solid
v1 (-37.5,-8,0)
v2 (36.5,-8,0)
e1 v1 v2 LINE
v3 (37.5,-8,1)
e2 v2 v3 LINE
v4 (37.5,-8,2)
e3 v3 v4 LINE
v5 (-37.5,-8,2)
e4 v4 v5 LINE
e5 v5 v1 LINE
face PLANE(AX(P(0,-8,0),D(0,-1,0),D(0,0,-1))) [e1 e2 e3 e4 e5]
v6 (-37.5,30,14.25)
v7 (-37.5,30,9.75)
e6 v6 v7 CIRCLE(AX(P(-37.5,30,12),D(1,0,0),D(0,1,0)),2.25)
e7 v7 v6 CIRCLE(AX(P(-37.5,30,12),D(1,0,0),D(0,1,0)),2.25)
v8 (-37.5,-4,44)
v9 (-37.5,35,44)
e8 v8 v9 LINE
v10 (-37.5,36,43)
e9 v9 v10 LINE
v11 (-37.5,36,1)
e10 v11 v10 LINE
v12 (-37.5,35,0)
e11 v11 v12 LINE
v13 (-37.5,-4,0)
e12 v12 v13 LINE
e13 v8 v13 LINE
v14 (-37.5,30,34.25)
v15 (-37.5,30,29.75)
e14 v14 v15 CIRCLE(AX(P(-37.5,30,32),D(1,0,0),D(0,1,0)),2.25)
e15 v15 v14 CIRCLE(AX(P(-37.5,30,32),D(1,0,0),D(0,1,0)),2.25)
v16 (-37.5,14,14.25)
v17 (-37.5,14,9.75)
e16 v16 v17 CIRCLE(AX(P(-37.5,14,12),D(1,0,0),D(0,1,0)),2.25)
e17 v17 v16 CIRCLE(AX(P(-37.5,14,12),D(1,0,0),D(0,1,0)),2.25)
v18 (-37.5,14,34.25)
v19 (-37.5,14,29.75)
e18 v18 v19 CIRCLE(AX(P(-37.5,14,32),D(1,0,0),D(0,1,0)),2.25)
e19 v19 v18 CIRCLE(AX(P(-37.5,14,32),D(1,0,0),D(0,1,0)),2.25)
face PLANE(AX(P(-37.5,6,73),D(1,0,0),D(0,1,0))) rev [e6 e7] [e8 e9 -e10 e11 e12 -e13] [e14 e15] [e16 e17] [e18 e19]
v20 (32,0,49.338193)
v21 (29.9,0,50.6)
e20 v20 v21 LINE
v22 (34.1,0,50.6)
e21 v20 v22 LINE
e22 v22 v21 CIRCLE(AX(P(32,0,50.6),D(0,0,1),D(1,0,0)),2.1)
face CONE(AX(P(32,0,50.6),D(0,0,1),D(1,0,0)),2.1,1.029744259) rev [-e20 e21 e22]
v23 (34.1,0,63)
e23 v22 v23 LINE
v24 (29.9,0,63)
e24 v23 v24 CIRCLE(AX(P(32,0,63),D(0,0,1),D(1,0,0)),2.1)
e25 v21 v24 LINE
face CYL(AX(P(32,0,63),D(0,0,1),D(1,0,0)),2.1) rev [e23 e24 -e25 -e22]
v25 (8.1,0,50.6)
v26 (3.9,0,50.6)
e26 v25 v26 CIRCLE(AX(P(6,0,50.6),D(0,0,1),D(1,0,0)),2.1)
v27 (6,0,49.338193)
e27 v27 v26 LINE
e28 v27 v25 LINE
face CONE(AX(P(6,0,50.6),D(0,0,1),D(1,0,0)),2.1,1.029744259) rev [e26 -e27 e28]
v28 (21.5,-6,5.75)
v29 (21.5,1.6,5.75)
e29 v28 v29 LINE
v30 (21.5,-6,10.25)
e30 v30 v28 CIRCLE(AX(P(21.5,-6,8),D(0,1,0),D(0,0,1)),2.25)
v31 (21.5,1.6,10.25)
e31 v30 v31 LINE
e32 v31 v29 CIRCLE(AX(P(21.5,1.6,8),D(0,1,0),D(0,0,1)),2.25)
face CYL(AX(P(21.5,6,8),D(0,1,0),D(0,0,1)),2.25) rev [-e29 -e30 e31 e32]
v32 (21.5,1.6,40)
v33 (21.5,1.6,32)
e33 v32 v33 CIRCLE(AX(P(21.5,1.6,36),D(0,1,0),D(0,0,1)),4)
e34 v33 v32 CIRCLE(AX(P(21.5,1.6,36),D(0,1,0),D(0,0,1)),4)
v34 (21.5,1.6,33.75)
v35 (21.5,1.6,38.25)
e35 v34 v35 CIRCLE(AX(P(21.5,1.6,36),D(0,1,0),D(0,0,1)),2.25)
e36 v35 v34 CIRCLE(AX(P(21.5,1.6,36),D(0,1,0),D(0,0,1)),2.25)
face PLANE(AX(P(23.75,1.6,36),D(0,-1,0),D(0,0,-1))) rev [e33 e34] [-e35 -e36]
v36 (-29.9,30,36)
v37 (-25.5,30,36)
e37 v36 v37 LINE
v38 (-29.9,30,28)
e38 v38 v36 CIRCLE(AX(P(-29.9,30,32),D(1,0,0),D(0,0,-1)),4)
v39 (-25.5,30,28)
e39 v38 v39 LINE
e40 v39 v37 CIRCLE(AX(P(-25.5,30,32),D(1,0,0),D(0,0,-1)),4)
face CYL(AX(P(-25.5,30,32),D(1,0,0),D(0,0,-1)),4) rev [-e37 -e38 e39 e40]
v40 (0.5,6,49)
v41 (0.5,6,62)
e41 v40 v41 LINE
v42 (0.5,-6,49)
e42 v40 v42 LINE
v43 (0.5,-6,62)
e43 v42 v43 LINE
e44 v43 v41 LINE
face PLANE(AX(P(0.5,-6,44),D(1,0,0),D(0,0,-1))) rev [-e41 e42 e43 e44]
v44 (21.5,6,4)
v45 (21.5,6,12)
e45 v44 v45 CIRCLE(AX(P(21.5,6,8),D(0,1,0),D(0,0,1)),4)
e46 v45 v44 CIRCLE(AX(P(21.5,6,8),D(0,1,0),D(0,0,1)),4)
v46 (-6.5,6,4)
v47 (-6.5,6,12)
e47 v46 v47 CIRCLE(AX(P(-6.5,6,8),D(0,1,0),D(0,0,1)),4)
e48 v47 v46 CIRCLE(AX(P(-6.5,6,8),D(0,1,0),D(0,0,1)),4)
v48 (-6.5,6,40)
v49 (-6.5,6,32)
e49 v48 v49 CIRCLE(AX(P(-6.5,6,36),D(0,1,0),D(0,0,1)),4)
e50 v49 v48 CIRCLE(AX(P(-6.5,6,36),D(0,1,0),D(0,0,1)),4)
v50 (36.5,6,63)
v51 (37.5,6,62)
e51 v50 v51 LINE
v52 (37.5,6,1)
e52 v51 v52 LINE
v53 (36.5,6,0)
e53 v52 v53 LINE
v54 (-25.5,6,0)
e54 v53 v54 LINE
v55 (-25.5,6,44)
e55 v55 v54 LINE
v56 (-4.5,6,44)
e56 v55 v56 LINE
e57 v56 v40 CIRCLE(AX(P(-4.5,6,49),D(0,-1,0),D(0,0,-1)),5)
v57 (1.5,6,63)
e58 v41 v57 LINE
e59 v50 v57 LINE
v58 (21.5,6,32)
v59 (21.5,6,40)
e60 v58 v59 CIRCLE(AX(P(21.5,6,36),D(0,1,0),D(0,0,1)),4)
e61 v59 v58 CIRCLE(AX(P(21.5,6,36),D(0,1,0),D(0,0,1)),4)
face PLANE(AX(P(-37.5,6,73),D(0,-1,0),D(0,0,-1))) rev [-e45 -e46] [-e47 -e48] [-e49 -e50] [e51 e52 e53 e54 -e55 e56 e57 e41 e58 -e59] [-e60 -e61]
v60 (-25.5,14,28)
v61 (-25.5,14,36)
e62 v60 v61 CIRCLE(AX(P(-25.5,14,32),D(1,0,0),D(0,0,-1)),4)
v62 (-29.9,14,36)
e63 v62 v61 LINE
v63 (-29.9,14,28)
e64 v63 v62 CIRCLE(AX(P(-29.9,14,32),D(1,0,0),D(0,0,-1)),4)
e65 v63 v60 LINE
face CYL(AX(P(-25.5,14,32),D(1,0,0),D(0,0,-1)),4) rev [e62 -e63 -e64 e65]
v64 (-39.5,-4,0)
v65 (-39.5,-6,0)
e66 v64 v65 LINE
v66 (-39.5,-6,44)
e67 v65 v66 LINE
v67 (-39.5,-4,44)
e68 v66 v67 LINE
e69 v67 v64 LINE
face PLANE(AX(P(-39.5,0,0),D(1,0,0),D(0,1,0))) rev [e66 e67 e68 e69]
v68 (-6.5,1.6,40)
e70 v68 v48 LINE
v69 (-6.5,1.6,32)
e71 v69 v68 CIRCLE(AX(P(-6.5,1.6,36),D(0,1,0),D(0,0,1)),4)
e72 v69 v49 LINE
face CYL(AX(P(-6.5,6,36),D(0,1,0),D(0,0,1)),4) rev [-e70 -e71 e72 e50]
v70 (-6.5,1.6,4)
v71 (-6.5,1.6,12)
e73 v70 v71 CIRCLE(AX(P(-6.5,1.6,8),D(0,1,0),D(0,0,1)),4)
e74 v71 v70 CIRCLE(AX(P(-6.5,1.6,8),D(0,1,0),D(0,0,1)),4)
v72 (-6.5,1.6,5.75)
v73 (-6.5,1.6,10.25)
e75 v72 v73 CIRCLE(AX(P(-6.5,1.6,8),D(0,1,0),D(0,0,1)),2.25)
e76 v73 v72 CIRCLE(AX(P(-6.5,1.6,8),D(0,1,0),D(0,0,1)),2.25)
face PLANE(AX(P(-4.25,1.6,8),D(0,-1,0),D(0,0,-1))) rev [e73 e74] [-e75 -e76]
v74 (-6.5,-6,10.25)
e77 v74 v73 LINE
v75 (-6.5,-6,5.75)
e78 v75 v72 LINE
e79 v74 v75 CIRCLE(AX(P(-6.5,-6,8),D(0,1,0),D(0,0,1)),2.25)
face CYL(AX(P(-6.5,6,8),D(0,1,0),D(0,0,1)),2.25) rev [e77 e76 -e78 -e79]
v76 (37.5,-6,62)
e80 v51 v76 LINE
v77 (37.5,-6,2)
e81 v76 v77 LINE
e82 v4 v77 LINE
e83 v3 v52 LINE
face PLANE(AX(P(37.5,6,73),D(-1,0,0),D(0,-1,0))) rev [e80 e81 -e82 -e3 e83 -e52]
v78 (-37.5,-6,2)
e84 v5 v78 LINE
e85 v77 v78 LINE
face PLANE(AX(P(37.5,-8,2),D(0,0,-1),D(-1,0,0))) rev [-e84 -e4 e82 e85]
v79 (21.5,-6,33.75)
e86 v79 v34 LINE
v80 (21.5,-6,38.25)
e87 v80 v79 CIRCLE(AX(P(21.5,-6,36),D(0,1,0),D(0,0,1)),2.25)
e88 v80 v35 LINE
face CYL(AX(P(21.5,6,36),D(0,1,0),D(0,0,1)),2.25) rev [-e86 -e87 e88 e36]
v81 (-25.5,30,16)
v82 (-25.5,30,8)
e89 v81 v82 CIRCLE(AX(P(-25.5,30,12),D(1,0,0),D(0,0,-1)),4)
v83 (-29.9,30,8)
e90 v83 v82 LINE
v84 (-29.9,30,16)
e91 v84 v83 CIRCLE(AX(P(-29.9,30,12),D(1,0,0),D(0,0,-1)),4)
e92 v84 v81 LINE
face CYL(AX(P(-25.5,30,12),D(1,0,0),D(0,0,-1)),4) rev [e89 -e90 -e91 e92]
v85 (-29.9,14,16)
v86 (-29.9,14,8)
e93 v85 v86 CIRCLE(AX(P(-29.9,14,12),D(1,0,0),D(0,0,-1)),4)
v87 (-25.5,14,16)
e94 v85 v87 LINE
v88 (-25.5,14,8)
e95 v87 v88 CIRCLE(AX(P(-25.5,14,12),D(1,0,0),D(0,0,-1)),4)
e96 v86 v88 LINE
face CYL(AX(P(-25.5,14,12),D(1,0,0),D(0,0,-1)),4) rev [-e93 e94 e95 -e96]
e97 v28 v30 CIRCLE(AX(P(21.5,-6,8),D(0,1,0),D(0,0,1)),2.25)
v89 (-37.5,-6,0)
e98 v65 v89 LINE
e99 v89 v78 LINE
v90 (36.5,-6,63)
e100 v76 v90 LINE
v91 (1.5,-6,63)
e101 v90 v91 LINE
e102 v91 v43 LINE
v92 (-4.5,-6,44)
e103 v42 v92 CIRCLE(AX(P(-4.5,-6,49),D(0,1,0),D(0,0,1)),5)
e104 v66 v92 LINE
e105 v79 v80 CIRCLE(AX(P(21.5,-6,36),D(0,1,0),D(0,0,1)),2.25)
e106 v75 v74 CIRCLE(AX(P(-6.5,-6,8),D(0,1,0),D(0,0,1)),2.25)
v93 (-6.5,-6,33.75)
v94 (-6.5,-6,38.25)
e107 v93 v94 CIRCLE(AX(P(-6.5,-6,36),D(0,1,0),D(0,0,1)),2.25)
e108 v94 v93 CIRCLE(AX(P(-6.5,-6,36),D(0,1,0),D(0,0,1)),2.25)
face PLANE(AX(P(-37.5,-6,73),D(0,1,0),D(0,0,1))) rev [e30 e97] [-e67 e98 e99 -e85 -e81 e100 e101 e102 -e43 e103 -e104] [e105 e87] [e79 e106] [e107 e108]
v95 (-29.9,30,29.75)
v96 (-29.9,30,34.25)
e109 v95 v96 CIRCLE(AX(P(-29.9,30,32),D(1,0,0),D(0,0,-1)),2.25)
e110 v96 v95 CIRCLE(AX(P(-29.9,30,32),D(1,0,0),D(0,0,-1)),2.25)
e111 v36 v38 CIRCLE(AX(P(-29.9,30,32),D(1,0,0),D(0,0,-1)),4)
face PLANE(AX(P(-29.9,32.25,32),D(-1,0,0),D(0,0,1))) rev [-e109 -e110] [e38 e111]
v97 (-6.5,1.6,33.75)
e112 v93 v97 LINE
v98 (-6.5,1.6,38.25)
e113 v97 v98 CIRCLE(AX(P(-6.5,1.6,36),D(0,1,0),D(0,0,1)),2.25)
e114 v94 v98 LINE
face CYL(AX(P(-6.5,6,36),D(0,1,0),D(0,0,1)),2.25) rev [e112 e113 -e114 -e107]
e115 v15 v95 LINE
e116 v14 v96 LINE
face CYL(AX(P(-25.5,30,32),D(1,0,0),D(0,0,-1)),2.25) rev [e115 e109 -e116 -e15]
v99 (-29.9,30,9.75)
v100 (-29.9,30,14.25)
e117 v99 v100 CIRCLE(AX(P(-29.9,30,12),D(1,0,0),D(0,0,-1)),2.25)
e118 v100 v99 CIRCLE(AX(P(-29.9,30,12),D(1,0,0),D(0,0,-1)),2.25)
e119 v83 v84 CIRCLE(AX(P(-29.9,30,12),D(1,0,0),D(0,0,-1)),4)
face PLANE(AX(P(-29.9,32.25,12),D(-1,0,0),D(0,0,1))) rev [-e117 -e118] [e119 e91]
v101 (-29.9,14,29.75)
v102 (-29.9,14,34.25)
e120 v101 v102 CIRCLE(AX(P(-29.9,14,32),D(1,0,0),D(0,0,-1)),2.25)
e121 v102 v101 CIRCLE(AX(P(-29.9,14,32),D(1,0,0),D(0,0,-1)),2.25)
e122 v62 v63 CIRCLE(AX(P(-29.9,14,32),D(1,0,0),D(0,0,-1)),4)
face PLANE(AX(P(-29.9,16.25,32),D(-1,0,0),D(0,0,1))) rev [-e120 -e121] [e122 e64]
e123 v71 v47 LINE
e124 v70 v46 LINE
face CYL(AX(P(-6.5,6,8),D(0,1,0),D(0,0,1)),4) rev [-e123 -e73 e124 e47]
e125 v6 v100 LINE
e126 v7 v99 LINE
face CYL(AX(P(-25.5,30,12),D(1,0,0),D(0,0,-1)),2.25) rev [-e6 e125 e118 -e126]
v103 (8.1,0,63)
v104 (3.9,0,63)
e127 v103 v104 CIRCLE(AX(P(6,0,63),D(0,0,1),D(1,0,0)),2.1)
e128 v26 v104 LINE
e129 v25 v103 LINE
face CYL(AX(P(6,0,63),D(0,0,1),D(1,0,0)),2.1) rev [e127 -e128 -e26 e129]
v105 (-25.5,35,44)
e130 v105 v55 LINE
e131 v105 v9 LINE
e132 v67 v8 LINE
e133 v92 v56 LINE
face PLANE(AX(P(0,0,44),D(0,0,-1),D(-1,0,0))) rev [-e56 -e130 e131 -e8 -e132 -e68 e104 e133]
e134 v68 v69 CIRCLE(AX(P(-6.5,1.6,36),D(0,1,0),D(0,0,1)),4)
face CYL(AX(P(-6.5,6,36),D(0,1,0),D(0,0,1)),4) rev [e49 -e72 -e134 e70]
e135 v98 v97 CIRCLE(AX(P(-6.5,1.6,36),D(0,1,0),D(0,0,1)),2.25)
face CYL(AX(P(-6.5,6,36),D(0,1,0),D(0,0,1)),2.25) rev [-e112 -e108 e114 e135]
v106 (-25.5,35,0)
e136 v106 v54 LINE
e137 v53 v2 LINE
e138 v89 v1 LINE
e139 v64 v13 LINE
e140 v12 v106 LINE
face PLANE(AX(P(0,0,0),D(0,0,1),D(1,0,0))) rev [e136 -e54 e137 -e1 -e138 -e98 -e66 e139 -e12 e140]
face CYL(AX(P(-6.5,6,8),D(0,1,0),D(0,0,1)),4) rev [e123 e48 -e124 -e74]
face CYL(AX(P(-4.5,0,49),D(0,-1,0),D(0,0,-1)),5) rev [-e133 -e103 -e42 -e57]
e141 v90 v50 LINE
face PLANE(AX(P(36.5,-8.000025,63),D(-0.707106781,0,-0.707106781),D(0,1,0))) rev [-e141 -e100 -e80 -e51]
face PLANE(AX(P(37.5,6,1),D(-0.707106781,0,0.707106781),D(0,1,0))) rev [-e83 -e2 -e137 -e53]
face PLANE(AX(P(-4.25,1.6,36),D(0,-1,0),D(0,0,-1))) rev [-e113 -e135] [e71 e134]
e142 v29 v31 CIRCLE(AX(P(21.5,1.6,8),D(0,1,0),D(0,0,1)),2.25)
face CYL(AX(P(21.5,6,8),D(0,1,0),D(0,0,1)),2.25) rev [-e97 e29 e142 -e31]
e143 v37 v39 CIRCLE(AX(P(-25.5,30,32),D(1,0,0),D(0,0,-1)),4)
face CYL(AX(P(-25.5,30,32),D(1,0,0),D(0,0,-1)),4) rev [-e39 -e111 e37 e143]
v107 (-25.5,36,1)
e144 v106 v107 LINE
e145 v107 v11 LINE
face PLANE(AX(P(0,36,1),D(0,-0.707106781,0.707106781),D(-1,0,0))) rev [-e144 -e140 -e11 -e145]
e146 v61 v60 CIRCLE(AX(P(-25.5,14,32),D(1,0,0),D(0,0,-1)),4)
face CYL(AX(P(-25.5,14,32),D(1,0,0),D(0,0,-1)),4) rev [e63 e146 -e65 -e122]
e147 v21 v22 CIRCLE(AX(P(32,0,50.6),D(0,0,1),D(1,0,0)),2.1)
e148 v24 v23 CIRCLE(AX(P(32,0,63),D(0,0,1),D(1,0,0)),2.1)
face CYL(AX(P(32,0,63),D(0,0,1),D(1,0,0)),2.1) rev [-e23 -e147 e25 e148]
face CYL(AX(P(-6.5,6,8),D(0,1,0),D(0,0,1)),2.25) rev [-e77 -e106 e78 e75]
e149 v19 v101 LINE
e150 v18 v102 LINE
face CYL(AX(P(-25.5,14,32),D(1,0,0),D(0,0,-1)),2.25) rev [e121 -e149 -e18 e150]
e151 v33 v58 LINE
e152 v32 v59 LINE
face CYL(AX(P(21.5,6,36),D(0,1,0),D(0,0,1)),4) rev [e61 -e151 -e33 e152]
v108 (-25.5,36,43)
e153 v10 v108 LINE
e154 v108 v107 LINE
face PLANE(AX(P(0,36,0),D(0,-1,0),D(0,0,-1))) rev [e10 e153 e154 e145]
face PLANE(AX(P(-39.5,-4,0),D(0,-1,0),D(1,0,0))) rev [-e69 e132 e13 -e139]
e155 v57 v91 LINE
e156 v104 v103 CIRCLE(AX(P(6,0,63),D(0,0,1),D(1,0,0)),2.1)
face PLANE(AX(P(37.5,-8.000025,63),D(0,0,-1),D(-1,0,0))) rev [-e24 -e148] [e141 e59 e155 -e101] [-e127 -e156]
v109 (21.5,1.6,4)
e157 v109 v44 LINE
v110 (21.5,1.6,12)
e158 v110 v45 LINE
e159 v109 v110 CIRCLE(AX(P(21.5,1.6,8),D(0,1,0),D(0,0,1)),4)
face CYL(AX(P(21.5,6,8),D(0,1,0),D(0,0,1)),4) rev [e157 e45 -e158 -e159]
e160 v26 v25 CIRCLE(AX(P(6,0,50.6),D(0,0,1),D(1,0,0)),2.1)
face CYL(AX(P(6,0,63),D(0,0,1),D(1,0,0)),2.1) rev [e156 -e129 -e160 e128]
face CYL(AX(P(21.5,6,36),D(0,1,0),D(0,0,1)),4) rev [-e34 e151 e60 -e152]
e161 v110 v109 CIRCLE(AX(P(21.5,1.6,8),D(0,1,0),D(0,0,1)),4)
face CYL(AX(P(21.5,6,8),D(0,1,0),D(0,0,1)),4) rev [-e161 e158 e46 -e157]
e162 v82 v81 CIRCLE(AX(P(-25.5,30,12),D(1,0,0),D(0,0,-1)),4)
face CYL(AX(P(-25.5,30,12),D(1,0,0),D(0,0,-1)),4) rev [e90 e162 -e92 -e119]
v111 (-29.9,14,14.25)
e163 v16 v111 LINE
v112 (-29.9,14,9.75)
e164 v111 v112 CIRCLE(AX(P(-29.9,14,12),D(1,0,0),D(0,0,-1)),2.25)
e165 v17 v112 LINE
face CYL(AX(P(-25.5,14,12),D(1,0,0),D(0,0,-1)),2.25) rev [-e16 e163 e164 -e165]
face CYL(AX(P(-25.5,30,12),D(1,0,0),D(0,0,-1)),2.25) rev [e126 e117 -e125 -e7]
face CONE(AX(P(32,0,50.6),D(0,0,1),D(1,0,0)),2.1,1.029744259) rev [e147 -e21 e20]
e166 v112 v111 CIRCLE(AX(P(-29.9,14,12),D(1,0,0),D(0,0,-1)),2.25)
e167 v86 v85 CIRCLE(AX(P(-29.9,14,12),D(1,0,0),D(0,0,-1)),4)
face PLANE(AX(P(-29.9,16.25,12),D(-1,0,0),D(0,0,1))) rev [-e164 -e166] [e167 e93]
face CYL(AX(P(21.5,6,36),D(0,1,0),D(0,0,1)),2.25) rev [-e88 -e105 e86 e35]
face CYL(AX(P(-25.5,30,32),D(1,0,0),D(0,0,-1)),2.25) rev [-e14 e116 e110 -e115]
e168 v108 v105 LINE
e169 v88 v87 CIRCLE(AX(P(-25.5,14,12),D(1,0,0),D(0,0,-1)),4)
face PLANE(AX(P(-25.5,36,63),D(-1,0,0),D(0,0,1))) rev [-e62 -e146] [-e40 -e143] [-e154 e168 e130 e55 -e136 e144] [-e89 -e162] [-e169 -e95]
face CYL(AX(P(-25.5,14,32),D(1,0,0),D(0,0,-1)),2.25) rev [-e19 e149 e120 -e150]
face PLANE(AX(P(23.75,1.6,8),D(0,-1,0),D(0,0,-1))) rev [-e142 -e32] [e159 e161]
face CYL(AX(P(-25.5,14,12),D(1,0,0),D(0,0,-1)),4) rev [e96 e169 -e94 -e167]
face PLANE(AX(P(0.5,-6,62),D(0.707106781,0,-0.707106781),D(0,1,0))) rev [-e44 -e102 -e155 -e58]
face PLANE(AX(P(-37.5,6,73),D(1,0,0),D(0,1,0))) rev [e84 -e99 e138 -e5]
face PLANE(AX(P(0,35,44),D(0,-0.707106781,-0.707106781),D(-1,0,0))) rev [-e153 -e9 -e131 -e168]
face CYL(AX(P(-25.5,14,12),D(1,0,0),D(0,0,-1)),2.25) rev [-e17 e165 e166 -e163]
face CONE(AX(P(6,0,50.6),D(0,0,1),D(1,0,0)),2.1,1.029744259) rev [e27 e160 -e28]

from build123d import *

# Parameters (mm, degrees)
SKETCH1_W                                           = 75
SKETCH1_H                                           = 12
BOSS_EXTRUDE1_DEPTH                                 = 73
SKETCH2_W                                           = 75
SKETCH2_H                                           = 2
BOSS_EXTRUDE2_DEPTH                                 = 2
SKETCH3_W                                           = 75
SKETCH3_H                                           = 10
BOSS_EXTRUDE3_DEPTH                                 = 15
SKETCH4_W                                           = 12
SKETCH4_H                                           = 63
BOSS_EXTRUDE4_DEPTH                                 = 30
SKETCH5_W                                           = 63
SKETCH5_H                                           = 2
BOSS_EXTRUDE5_DEPTH                                 = 2
SKETCH7_W                                           = 40
SKETCH7_H                                           = 42
CUT_EXTRUDE2_DEPTH                                  = 29
M5_TAPPED_HOLE1_D                                   = 4.2
M5_TAPPED_HOLE1_DEPTH                               = 12.4
M5_TAPPED_HOLE1_TIP                                 = 1.2618073
CBORE_FOR_M4_HEX_SOCKET_HEAD_CAP_SCREW1_D           = 4.5
CBORE_FOR_M4_HEX_SOCKET_HEAD_CAP_SCREW1_CBORE_D     = 8
CBORE_FOR_M4_HEX_SOCKET_HEAD_CAP_SCREW1_CBORE_DEPTH = 4.4
SKETCH12_W                                          = 37
SKETCH12_H                                          = 10
CUT_EXTRUDE3_DEPTH                                  = 88.92184029
M5_TAPPED_HOLE2_D                                   = 4.2
M5_TAPPED_HOLE2_DEPTH                               = 12.4
M5_TAPPED_HOLE2_TIP                                 = 1.2618073
FILLET1_R                                           = 5
CBORE_FOR_M4_HEX_SOCKET_HEAD_CAP_SCREW2_D           = 4.5
CBORE_FOR_M4_HEX_SOCKET_HEAD_CAP_SCREW2_CBORE_D     = 8
CBORE_FOR_M4_HEX_SOCKET_HEAD_CAP_SCREW2_CBORE_DEPTH = 4.4
CHAMFER1_SIZE                                       = 1


with BuildPart() as part:
    # Sketch1 → Boss-Extrude1 (new body)
    with BuildSketch(Plane.XY):
        Rectangle(SKETCH1_W, SKETCH1_H)
    extrude(amount=BOSS_EXTRUDE1_DEPTH)

    # Sketch2 → Boss-Extrude2 (add)
    with BuildSketch(Plane.XZ.offset(6)):
        with Locations((0, 1)):
            Rectangle(SKETCH2_W, SKETCH2_H)
    extrude(amount=BOSS_EXTRUDE2_DEPTH)

    # Sketch3 → Boss-Extrude3 (add)
    with BuildSketch(Plane(origin=(0, 6, 0), x_dir=(1, 0, 0), z_dir=(0, 1, 0))):
        with Locations((0, -68)):
            Rectangle(SKETCH3_W, SKETCH3_H)
    extrude(amount=BOSS_EXTRUDE3_DEPTH)

    # Sketch4 → Boss-Extrude4 (add)
    with BuildSketch(Plane(origin=(0, 6, 0), x_dir=(1, 0, 0), z_dir=(0, 1, 0))):
        with Locations((-31.5, -31.5)):
            Rectangle(SKETCH4_W, SKETCH4_H)
    extrude(amount=BOSS_EXTRUDE4_DEPTH)

    # Sketch5 → Boss-Extrude5 (add)
    with BuildSketch(Plane.ZY.offset(37.5)):
        with Locations((31.5, -5)):
            Rectangle(SKETCH5_W, SKETCH5_H)
    extrude(amount=BOSS_EXTRUDE5_DEPTH)

    # Sketch7 → Cut-Extrude2 (cut)
    with BuildSketch(Plane.XY.offset(73)):
        with Locations((-19.5, 15)):
            Rectangle(SKETCH7_W, SKETCH7_H)
    extrude(amount=-CUT_EXTRUDE2_DEPTH, mode=Mode.SUBTRACT)

    # M5 Tapped Hole1
    with Locations(Plane.XY.offset(73)):
        with Locations((19, 10)):
            Hole(M5_TAPPED_HOLE1_D / 2, depth=M5_TAPPED_HOLE1_DEPTH)
            with Locations((0, 0, -(M5_TAPPED_HOLE1_DEPTH + M5_TAPPED_HOLE1_TIP / 2))):  # 118° drill point
                Cone(0, M5_TAPPED_HOLE1_D / 2, M5_TAPPED_HOLE1_TIP, mode=Mode.SUBTRACT)

    # CBORE for M4 Hex Socket Head Cap Screw1 (through all)
    with Locations(Plane(origin=(-25.5, 0, 0), x_dir=(0, 0, -1), z_dir=(1, 0, 0))):
        with Locations((-32, 30), (-32, 14), (-12, 14), (-12, 30)):
            CounterBoreHole(CBORE_FOR_M4_HEX_SOCKET_HEAD_CAP_SCREW1_D / 2, CBORE_FOR_M4_HEX_SOCKET_HEAD_CAP_SCREW1_CBORE_D / 2, CBORE_FOR_M4_HEX_SOCKET_HEAD_CAP_SCREW1_CBORE_DEPTH)

    # Sketch12 → Cut-Extrude3 (cut, through all)
    with BuildSketch(Plane(origin=(0, 21, 0), x_dir=(1, 0, 0), z_dir=(0, 1, 0))):
        with Locations((19, -68)):
            Rectangle(SKETCH12_W, SKETCH12_H)
    extrude(amount=-CUT_EXTRUDE3_DEPTH, mode=Mode.SUBTRACT)

    # M5 Tapped Hole2
    with Locations(Plane.XY.offset(63)):
        with Locations((32, 0), (6, 0)):
            Hole(M5_TAPPED_HOLE2_D / 2, depth=M5_TAPPED_HOLE2_DEPTH)
            with Locations((0, 0, -(M5_TAPPED_HOLE2_DEPTH + M5_TAPPED_HOLE2_TIP / 2))):  # 118° drill point
                Cone(0, M5_TAPPED_HOLE2_D / 2, M5_TAPPED_HOLE2_TIP, mode=Mode.SUBTRACT)

    # Fillet1
    fillet1_edges = [part.edges().sort_by_distance(p)[0] for p in [
        (0.5, 0, 44),
    ]]
    fillet(fillet1_edges, radius=FILLET1_R)

    # CBORE for M4 Hex Socket Head Cap Screw2 (through all)
    with Locations(Plane(origin=(0, 6, 0), x_dir=(1, 0, 0), z_dir=(0, 1, 0))):
        with Locations((-6.5, -8), (21.5, -8), (-6.5, -36), (21.5, -36)):
            CounterBoreHole(CBORE_FOR_M4_HEX_SOCKET_HEAD_CAP_SCREW2_D / 2, CBORE_FOR_M4_HEX_SOCKET_HEAD_CAP_SCREW2_CBORE_D / 2, CBORE_FOR_M4_HEX_SOCKET_HEAD_CAP_SCREW2_CBORE_DEPTH)

    # Chamfer1
    chamfer1_edges = [part.edges().sort_by_distance(p)[0] for p in [
        (0.5, 0, 63),
        (37.5, 0, 63),
        (37.5, -1, 0),
        (-31.5, 36, 0),
        (-31.5, 36, 44),
    ]]
    chamfer(chamfer1_edges, length=CHAMFER1_SIZE)


solid = part.part
